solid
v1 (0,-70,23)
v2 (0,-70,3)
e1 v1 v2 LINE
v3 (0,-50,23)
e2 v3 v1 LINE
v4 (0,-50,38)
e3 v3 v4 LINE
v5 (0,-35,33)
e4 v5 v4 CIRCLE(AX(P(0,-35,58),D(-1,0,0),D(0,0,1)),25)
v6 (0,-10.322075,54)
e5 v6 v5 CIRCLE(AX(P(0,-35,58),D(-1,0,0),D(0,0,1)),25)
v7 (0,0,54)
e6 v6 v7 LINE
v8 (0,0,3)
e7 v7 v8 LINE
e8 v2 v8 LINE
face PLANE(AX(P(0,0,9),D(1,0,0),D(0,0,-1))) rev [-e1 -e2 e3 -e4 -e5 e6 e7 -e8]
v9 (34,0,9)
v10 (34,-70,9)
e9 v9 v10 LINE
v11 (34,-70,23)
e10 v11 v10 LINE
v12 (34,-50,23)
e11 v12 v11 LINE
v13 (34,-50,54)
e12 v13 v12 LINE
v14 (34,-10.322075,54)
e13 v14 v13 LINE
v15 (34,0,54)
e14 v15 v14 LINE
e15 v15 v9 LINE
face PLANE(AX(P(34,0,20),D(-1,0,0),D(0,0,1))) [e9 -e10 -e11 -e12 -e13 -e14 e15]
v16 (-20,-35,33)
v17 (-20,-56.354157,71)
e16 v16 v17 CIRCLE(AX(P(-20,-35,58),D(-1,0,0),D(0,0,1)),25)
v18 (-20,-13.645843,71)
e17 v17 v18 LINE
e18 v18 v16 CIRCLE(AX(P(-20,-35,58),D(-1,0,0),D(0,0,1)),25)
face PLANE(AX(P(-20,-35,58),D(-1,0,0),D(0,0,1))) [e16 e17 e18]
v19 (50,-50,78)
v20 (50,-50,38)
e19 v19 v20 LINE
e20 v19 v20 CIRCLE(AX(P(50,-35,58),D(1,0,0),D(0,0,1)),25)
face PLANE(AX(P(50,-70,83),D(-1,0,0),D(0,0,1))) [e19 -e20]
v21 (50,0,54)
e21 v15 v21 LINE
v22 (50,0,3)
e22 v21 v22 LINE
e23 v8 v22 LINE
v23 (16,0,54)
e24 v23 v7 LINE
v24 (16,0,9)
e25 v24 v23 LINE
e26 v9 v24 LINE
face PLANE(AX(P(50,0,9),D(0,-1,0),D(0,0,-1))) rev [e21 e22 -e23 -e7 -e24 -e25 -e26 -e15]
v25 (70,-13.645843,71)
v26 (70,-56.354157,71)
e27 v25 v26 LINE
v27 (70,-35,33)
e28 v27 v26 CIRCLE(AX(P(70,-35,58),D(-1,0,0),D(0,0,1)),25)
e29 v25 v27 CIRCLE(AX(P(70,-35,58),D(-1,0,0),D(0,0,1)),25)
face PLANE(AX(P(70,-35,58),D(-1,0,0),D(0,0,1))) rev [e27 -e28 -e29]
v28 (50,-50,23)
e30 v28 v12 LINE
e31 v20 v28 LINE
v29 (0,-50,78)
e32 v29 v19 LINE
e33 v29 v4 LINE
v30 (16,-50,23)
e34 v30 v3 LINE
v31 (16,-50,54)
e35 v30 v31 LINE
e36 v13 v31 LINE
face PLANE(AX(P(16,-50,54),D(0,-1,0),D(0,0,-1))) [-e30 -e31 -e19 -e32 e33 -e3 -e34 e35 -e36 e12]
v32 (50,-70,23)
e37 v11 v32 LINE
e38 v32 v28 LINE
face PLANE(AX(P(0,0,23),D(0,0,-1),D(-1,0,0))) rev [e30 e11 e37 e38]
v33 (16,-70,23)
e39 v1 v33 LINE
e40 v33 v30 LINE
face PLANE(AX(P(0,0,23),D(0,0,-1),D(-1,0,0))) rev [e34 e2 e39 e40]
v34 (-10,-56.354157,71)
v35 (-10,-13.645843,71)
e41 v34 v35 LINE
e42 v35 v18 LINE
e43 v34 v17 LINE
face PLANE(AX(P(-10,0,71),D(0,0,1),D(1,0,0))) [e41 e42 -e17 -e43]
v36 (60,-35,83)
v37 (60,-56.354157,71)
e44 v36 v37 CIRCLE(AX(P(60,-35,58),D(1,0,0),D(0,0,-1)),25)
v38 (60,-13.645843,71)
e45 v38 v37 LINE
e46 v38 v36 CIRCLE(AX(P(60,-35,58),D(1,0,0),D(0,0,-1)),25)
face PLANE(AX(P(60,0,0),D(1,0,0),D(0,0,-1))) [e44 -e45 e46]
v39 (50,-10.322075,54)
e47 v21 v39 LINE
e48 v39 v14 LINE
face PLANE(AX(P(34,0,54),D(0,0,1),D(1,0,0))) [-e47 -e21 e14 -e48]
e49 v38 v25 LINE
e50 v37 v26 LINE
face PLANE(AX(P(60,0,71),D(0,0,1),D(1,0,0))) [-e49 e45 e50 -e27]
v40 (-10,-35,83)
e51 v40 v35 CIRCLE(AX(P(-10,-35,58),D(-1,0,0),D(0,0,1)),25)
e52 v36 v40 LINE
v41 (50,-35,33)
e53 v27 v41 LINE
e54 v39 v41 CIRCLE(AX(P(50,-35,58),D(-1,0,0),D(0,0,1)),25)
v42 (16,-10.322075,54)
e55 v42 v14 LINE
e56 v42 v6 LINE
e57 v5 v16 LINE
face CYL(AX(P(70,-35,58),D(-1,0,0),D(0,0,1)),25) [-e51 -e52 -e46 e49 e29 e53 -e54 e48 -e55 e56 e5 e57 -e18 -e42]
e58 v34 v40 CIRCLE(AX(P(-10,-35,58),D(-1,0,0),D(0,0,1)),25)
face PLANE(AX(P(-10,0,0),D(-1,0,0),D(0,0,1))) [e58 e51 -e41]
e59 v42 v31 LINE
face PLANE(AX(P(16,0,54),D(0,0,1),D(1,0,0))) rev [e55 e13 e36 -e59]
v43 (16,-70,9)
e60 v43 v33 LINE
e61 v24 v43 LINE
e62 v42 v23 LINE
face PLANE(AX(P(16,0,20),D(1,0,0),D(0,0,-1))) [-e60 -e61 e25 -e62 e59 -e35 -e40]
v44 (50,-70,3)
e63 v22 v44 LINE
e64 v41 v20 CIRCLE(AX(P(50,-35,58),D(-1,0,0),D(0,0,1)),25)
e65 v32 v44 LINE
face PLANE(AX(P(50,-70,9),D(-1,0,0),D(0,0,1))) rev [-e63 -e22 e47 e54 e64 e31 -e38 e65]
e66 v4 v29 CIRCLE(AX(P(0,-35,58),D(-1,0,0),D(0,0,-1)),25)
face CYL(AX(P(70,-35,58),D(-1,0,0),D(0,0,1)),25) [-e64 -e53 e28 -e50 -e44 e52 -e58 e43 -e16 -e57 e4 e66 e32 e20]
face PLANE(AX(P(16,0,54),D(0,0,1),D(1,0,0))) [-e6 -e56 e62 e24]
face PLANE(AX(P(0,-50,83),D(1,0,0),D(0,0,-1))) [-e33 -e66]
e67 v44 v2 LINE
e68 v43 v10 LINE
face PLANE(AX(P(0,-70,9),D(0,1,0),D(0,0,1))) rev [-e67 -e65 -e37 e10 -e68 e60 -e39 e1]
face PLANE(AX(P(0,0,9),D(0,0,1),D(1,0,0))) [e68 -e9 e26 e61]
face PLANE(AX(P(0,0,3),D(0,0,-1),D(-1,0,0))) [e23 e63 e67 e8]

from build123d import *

# Parameters (mm, degrees)
BASE_PLATE_SKETCH_W         = 50
BASE_PLATE_SKETCH_H         = 70
BASE_PLATE_DEPTH            = 9
U_FRAME_SKETCH_W            = 16
U_FRAME_SKETCH_H            = 11
U_FRAME_DEPTH               = 70
SIDE_BLOCK_A_SKETCH_W       = 34
SIDE_BLOCK_A_SKETCH_H       = 50
SIDE_BLOCK_A_DEPTH          = 16
SIDE_BLOCK_B_SKETCH_W       = 34
SIDE_BLOCK_B_SKETCH_H       = 50
SIDE_BLOCK_B_DEPTH          = 16
BASE_RECESS_SKETCH_W        = 50
BASE_RECESS_SKETCH_H        = 70
BASE_RECESS_CUT_DEPTH       = 3
TOP_LIP_SKETCH_W            = 16
TOP_LIP_SKETCH_H            = 20
TOP_LIP_DEPTH               = 3
CYLINDER_SKETCH_R           = 25
CYLINDER_50_DEPTH           = 70
CYLINDER_START              = 20
CYLINDER_EXTENSION_SKETCH_R = 25
CYLINDER_EXTENSION_50_DEPTH = 20
U_SLOT_CUT_DEPTH            = 60
FRAME_CLEARANCE_SKETCH_W    = 18
FRAME_CLEARANCE_SKETCH_H    = 21
FRAME_CLEARANCE_CUT_DEPTH   = 50
END_FLAT_A_DEPTH            = 10
END_START                   = -10
END_FLAT_B_DEPTH            = 10


with BuildPart() as part:
    # Base Plate Sketch → Base Plate (new body)
    with BuildSketch(Plane.XY):
        with Locations((25, -35)):
            Rectangle(BASE_PLATE_SKETCH_W, BASE_PLATE_SKETCH_H)
    extrude(amount=BASE_PLATE_DEPTH)

    # U-Frame Sketch → U-Frame (add)
    with BuildSketch(Plane.XZ.offset(70)):
        with Locations((8, 14.5)):
            Rectangle(U_FRAME_SKETCH_W, U_FRAME_SKETCH_H)
        with Locations((42, 14.5)):
            Rectangle(U_FRAME_SKETCH_W, U_FRAME_SKETCH_H)
    extrude(amount=-U_FRAME_DEPTH)

    # Side Block A Sketch → Side Block A (add)
    with BuildSketch(Plane.ZY):
        with Locations((37, -25)):
            Rectangle(SIDE_BLOCK_A_SKETCH_W, SIDE_BLOCK_A_SKETCH_H)
    extrude(amount=-SIDE_BLOCK_A_DEPTH)

    # Side Block B Sketch → Side Block B (add)
    with BuildSketch(Plane(origin=(50, 0, 0), x_dir=(0, 0, -1), z_dir=(1, 0, 0))):
        with Locations((-37, -25)):
            Rectangle(SIDE_BLOCK_B_SKETCH_W, SIDE_BLOCK_B_SKETCH_H)
    extrude(amount=-SIDE_BLOCK_B_DEPTH)

    # Base Recess Sketch → Base Recess Cut (cut)
    with BuildSketch(Plane(origin=(0, 0, 0), x_dir=(-1, 0, 0), z_dir=(0, 0, -1))):
        with Locations((-25, -35)):
            Rectangle(BASE_RECESS_SKETCH_W, BASE_RECESS_SKETCH_H)
    extrude(amount=-BASE_RECESS_CUT_DEPTH, mode=Mode.SUBTRACT)

    # Top Lip Sketch → Top Lip (add)
    with BuildSketch(Plane.XY.offset(20)):
        with Locations((8, -60)):
            Rectangle(TOP_LIP_SKETCH_W, TOP_LIP_SKETCH_H)
        with Locations((42, -60)):
            Rectangle(TOP_LIP_SKETCH_W, TOP_LIP_SKETCH_H)
    extrude(amount=TOP_LIP_DEPTH)

    # Cylinder Sketch → Cylinder Ø50 (add)
    with BuildSketch(Plane.ZY):
        with Locations((58, -35)):
            Circle(CYLINDER_SKETCH_R)
    extrude(amount=-CYLINDER_50_DEPTH)

    # Cylinder Extension Sketch → Cylinder Extension Ø50 (add)
    with BuildSketch(Plane.ZY.offset(CYLINDER_START)):
        with Locations((58, -35)):
            Circle(CYLINDER_EXTENSION_SKETCH_R)
    extrude(amount=-CYLINDER_EXTENSION_50_DEPTH)

    # U-Slot Sketch → U-Slot Cut (cut)
    with BuildSketch(Plane.XY.offset(23)):
        Polygon((34, -70), (50, -70), (50, -50), (0, -50), (0, -70), align=None)
    extrude(amount=U_SLOT_CUT_DEPTH, mode=Mode.SUBTRACT)

    # Frame Clearance Sketch → Frame Clearance Cut (cut)
    with BuildSketch(Plane.XZ.offset(50)):
        with Locations((25, 43.5)):
            Rectangle(FRAME_CLEARANCE_SKETCH_W, FRAME_CLEARANCE_SKETCH_H)
    extrude(amount=-FRAME_CLEARANCE_CUT_DEPTH, mode=Mode.SUBTRACT)

    # End Flat A Sketch → End Flat A (cut)
    with BuildSketch(Plane.ZY.offset(20)):
        with BuildLine():
            Line((71, -13.645843496), (71, -56.354156504))
            ThreePointArc((71, -56.354156504), (83, -35), (71, -13.645843496))
        make_face()
    extrude(amount=-END_FLAT_A_DEPTH, mode=Mode.SUBTRACT)

    # End Flat B Sketch → End Flat B (cut)
    with BuildSketch(Plane(origin=(70, 0, 0), x_dir=(0, 0, -1), z_dir=(1, 0, 0)).offset(END_START)):
        with BuildLine():
            Line((-71, -13.645843496), (-71, -56.354156504))
            ThreePointArc((-71, -56.354156504), (-83, -35), (-71, -13.645843496))
        make_face()
    extrude(amount=END_FLAT_B_DEPTH, mode=Mode.SUBTRACT)


solid = part.part
